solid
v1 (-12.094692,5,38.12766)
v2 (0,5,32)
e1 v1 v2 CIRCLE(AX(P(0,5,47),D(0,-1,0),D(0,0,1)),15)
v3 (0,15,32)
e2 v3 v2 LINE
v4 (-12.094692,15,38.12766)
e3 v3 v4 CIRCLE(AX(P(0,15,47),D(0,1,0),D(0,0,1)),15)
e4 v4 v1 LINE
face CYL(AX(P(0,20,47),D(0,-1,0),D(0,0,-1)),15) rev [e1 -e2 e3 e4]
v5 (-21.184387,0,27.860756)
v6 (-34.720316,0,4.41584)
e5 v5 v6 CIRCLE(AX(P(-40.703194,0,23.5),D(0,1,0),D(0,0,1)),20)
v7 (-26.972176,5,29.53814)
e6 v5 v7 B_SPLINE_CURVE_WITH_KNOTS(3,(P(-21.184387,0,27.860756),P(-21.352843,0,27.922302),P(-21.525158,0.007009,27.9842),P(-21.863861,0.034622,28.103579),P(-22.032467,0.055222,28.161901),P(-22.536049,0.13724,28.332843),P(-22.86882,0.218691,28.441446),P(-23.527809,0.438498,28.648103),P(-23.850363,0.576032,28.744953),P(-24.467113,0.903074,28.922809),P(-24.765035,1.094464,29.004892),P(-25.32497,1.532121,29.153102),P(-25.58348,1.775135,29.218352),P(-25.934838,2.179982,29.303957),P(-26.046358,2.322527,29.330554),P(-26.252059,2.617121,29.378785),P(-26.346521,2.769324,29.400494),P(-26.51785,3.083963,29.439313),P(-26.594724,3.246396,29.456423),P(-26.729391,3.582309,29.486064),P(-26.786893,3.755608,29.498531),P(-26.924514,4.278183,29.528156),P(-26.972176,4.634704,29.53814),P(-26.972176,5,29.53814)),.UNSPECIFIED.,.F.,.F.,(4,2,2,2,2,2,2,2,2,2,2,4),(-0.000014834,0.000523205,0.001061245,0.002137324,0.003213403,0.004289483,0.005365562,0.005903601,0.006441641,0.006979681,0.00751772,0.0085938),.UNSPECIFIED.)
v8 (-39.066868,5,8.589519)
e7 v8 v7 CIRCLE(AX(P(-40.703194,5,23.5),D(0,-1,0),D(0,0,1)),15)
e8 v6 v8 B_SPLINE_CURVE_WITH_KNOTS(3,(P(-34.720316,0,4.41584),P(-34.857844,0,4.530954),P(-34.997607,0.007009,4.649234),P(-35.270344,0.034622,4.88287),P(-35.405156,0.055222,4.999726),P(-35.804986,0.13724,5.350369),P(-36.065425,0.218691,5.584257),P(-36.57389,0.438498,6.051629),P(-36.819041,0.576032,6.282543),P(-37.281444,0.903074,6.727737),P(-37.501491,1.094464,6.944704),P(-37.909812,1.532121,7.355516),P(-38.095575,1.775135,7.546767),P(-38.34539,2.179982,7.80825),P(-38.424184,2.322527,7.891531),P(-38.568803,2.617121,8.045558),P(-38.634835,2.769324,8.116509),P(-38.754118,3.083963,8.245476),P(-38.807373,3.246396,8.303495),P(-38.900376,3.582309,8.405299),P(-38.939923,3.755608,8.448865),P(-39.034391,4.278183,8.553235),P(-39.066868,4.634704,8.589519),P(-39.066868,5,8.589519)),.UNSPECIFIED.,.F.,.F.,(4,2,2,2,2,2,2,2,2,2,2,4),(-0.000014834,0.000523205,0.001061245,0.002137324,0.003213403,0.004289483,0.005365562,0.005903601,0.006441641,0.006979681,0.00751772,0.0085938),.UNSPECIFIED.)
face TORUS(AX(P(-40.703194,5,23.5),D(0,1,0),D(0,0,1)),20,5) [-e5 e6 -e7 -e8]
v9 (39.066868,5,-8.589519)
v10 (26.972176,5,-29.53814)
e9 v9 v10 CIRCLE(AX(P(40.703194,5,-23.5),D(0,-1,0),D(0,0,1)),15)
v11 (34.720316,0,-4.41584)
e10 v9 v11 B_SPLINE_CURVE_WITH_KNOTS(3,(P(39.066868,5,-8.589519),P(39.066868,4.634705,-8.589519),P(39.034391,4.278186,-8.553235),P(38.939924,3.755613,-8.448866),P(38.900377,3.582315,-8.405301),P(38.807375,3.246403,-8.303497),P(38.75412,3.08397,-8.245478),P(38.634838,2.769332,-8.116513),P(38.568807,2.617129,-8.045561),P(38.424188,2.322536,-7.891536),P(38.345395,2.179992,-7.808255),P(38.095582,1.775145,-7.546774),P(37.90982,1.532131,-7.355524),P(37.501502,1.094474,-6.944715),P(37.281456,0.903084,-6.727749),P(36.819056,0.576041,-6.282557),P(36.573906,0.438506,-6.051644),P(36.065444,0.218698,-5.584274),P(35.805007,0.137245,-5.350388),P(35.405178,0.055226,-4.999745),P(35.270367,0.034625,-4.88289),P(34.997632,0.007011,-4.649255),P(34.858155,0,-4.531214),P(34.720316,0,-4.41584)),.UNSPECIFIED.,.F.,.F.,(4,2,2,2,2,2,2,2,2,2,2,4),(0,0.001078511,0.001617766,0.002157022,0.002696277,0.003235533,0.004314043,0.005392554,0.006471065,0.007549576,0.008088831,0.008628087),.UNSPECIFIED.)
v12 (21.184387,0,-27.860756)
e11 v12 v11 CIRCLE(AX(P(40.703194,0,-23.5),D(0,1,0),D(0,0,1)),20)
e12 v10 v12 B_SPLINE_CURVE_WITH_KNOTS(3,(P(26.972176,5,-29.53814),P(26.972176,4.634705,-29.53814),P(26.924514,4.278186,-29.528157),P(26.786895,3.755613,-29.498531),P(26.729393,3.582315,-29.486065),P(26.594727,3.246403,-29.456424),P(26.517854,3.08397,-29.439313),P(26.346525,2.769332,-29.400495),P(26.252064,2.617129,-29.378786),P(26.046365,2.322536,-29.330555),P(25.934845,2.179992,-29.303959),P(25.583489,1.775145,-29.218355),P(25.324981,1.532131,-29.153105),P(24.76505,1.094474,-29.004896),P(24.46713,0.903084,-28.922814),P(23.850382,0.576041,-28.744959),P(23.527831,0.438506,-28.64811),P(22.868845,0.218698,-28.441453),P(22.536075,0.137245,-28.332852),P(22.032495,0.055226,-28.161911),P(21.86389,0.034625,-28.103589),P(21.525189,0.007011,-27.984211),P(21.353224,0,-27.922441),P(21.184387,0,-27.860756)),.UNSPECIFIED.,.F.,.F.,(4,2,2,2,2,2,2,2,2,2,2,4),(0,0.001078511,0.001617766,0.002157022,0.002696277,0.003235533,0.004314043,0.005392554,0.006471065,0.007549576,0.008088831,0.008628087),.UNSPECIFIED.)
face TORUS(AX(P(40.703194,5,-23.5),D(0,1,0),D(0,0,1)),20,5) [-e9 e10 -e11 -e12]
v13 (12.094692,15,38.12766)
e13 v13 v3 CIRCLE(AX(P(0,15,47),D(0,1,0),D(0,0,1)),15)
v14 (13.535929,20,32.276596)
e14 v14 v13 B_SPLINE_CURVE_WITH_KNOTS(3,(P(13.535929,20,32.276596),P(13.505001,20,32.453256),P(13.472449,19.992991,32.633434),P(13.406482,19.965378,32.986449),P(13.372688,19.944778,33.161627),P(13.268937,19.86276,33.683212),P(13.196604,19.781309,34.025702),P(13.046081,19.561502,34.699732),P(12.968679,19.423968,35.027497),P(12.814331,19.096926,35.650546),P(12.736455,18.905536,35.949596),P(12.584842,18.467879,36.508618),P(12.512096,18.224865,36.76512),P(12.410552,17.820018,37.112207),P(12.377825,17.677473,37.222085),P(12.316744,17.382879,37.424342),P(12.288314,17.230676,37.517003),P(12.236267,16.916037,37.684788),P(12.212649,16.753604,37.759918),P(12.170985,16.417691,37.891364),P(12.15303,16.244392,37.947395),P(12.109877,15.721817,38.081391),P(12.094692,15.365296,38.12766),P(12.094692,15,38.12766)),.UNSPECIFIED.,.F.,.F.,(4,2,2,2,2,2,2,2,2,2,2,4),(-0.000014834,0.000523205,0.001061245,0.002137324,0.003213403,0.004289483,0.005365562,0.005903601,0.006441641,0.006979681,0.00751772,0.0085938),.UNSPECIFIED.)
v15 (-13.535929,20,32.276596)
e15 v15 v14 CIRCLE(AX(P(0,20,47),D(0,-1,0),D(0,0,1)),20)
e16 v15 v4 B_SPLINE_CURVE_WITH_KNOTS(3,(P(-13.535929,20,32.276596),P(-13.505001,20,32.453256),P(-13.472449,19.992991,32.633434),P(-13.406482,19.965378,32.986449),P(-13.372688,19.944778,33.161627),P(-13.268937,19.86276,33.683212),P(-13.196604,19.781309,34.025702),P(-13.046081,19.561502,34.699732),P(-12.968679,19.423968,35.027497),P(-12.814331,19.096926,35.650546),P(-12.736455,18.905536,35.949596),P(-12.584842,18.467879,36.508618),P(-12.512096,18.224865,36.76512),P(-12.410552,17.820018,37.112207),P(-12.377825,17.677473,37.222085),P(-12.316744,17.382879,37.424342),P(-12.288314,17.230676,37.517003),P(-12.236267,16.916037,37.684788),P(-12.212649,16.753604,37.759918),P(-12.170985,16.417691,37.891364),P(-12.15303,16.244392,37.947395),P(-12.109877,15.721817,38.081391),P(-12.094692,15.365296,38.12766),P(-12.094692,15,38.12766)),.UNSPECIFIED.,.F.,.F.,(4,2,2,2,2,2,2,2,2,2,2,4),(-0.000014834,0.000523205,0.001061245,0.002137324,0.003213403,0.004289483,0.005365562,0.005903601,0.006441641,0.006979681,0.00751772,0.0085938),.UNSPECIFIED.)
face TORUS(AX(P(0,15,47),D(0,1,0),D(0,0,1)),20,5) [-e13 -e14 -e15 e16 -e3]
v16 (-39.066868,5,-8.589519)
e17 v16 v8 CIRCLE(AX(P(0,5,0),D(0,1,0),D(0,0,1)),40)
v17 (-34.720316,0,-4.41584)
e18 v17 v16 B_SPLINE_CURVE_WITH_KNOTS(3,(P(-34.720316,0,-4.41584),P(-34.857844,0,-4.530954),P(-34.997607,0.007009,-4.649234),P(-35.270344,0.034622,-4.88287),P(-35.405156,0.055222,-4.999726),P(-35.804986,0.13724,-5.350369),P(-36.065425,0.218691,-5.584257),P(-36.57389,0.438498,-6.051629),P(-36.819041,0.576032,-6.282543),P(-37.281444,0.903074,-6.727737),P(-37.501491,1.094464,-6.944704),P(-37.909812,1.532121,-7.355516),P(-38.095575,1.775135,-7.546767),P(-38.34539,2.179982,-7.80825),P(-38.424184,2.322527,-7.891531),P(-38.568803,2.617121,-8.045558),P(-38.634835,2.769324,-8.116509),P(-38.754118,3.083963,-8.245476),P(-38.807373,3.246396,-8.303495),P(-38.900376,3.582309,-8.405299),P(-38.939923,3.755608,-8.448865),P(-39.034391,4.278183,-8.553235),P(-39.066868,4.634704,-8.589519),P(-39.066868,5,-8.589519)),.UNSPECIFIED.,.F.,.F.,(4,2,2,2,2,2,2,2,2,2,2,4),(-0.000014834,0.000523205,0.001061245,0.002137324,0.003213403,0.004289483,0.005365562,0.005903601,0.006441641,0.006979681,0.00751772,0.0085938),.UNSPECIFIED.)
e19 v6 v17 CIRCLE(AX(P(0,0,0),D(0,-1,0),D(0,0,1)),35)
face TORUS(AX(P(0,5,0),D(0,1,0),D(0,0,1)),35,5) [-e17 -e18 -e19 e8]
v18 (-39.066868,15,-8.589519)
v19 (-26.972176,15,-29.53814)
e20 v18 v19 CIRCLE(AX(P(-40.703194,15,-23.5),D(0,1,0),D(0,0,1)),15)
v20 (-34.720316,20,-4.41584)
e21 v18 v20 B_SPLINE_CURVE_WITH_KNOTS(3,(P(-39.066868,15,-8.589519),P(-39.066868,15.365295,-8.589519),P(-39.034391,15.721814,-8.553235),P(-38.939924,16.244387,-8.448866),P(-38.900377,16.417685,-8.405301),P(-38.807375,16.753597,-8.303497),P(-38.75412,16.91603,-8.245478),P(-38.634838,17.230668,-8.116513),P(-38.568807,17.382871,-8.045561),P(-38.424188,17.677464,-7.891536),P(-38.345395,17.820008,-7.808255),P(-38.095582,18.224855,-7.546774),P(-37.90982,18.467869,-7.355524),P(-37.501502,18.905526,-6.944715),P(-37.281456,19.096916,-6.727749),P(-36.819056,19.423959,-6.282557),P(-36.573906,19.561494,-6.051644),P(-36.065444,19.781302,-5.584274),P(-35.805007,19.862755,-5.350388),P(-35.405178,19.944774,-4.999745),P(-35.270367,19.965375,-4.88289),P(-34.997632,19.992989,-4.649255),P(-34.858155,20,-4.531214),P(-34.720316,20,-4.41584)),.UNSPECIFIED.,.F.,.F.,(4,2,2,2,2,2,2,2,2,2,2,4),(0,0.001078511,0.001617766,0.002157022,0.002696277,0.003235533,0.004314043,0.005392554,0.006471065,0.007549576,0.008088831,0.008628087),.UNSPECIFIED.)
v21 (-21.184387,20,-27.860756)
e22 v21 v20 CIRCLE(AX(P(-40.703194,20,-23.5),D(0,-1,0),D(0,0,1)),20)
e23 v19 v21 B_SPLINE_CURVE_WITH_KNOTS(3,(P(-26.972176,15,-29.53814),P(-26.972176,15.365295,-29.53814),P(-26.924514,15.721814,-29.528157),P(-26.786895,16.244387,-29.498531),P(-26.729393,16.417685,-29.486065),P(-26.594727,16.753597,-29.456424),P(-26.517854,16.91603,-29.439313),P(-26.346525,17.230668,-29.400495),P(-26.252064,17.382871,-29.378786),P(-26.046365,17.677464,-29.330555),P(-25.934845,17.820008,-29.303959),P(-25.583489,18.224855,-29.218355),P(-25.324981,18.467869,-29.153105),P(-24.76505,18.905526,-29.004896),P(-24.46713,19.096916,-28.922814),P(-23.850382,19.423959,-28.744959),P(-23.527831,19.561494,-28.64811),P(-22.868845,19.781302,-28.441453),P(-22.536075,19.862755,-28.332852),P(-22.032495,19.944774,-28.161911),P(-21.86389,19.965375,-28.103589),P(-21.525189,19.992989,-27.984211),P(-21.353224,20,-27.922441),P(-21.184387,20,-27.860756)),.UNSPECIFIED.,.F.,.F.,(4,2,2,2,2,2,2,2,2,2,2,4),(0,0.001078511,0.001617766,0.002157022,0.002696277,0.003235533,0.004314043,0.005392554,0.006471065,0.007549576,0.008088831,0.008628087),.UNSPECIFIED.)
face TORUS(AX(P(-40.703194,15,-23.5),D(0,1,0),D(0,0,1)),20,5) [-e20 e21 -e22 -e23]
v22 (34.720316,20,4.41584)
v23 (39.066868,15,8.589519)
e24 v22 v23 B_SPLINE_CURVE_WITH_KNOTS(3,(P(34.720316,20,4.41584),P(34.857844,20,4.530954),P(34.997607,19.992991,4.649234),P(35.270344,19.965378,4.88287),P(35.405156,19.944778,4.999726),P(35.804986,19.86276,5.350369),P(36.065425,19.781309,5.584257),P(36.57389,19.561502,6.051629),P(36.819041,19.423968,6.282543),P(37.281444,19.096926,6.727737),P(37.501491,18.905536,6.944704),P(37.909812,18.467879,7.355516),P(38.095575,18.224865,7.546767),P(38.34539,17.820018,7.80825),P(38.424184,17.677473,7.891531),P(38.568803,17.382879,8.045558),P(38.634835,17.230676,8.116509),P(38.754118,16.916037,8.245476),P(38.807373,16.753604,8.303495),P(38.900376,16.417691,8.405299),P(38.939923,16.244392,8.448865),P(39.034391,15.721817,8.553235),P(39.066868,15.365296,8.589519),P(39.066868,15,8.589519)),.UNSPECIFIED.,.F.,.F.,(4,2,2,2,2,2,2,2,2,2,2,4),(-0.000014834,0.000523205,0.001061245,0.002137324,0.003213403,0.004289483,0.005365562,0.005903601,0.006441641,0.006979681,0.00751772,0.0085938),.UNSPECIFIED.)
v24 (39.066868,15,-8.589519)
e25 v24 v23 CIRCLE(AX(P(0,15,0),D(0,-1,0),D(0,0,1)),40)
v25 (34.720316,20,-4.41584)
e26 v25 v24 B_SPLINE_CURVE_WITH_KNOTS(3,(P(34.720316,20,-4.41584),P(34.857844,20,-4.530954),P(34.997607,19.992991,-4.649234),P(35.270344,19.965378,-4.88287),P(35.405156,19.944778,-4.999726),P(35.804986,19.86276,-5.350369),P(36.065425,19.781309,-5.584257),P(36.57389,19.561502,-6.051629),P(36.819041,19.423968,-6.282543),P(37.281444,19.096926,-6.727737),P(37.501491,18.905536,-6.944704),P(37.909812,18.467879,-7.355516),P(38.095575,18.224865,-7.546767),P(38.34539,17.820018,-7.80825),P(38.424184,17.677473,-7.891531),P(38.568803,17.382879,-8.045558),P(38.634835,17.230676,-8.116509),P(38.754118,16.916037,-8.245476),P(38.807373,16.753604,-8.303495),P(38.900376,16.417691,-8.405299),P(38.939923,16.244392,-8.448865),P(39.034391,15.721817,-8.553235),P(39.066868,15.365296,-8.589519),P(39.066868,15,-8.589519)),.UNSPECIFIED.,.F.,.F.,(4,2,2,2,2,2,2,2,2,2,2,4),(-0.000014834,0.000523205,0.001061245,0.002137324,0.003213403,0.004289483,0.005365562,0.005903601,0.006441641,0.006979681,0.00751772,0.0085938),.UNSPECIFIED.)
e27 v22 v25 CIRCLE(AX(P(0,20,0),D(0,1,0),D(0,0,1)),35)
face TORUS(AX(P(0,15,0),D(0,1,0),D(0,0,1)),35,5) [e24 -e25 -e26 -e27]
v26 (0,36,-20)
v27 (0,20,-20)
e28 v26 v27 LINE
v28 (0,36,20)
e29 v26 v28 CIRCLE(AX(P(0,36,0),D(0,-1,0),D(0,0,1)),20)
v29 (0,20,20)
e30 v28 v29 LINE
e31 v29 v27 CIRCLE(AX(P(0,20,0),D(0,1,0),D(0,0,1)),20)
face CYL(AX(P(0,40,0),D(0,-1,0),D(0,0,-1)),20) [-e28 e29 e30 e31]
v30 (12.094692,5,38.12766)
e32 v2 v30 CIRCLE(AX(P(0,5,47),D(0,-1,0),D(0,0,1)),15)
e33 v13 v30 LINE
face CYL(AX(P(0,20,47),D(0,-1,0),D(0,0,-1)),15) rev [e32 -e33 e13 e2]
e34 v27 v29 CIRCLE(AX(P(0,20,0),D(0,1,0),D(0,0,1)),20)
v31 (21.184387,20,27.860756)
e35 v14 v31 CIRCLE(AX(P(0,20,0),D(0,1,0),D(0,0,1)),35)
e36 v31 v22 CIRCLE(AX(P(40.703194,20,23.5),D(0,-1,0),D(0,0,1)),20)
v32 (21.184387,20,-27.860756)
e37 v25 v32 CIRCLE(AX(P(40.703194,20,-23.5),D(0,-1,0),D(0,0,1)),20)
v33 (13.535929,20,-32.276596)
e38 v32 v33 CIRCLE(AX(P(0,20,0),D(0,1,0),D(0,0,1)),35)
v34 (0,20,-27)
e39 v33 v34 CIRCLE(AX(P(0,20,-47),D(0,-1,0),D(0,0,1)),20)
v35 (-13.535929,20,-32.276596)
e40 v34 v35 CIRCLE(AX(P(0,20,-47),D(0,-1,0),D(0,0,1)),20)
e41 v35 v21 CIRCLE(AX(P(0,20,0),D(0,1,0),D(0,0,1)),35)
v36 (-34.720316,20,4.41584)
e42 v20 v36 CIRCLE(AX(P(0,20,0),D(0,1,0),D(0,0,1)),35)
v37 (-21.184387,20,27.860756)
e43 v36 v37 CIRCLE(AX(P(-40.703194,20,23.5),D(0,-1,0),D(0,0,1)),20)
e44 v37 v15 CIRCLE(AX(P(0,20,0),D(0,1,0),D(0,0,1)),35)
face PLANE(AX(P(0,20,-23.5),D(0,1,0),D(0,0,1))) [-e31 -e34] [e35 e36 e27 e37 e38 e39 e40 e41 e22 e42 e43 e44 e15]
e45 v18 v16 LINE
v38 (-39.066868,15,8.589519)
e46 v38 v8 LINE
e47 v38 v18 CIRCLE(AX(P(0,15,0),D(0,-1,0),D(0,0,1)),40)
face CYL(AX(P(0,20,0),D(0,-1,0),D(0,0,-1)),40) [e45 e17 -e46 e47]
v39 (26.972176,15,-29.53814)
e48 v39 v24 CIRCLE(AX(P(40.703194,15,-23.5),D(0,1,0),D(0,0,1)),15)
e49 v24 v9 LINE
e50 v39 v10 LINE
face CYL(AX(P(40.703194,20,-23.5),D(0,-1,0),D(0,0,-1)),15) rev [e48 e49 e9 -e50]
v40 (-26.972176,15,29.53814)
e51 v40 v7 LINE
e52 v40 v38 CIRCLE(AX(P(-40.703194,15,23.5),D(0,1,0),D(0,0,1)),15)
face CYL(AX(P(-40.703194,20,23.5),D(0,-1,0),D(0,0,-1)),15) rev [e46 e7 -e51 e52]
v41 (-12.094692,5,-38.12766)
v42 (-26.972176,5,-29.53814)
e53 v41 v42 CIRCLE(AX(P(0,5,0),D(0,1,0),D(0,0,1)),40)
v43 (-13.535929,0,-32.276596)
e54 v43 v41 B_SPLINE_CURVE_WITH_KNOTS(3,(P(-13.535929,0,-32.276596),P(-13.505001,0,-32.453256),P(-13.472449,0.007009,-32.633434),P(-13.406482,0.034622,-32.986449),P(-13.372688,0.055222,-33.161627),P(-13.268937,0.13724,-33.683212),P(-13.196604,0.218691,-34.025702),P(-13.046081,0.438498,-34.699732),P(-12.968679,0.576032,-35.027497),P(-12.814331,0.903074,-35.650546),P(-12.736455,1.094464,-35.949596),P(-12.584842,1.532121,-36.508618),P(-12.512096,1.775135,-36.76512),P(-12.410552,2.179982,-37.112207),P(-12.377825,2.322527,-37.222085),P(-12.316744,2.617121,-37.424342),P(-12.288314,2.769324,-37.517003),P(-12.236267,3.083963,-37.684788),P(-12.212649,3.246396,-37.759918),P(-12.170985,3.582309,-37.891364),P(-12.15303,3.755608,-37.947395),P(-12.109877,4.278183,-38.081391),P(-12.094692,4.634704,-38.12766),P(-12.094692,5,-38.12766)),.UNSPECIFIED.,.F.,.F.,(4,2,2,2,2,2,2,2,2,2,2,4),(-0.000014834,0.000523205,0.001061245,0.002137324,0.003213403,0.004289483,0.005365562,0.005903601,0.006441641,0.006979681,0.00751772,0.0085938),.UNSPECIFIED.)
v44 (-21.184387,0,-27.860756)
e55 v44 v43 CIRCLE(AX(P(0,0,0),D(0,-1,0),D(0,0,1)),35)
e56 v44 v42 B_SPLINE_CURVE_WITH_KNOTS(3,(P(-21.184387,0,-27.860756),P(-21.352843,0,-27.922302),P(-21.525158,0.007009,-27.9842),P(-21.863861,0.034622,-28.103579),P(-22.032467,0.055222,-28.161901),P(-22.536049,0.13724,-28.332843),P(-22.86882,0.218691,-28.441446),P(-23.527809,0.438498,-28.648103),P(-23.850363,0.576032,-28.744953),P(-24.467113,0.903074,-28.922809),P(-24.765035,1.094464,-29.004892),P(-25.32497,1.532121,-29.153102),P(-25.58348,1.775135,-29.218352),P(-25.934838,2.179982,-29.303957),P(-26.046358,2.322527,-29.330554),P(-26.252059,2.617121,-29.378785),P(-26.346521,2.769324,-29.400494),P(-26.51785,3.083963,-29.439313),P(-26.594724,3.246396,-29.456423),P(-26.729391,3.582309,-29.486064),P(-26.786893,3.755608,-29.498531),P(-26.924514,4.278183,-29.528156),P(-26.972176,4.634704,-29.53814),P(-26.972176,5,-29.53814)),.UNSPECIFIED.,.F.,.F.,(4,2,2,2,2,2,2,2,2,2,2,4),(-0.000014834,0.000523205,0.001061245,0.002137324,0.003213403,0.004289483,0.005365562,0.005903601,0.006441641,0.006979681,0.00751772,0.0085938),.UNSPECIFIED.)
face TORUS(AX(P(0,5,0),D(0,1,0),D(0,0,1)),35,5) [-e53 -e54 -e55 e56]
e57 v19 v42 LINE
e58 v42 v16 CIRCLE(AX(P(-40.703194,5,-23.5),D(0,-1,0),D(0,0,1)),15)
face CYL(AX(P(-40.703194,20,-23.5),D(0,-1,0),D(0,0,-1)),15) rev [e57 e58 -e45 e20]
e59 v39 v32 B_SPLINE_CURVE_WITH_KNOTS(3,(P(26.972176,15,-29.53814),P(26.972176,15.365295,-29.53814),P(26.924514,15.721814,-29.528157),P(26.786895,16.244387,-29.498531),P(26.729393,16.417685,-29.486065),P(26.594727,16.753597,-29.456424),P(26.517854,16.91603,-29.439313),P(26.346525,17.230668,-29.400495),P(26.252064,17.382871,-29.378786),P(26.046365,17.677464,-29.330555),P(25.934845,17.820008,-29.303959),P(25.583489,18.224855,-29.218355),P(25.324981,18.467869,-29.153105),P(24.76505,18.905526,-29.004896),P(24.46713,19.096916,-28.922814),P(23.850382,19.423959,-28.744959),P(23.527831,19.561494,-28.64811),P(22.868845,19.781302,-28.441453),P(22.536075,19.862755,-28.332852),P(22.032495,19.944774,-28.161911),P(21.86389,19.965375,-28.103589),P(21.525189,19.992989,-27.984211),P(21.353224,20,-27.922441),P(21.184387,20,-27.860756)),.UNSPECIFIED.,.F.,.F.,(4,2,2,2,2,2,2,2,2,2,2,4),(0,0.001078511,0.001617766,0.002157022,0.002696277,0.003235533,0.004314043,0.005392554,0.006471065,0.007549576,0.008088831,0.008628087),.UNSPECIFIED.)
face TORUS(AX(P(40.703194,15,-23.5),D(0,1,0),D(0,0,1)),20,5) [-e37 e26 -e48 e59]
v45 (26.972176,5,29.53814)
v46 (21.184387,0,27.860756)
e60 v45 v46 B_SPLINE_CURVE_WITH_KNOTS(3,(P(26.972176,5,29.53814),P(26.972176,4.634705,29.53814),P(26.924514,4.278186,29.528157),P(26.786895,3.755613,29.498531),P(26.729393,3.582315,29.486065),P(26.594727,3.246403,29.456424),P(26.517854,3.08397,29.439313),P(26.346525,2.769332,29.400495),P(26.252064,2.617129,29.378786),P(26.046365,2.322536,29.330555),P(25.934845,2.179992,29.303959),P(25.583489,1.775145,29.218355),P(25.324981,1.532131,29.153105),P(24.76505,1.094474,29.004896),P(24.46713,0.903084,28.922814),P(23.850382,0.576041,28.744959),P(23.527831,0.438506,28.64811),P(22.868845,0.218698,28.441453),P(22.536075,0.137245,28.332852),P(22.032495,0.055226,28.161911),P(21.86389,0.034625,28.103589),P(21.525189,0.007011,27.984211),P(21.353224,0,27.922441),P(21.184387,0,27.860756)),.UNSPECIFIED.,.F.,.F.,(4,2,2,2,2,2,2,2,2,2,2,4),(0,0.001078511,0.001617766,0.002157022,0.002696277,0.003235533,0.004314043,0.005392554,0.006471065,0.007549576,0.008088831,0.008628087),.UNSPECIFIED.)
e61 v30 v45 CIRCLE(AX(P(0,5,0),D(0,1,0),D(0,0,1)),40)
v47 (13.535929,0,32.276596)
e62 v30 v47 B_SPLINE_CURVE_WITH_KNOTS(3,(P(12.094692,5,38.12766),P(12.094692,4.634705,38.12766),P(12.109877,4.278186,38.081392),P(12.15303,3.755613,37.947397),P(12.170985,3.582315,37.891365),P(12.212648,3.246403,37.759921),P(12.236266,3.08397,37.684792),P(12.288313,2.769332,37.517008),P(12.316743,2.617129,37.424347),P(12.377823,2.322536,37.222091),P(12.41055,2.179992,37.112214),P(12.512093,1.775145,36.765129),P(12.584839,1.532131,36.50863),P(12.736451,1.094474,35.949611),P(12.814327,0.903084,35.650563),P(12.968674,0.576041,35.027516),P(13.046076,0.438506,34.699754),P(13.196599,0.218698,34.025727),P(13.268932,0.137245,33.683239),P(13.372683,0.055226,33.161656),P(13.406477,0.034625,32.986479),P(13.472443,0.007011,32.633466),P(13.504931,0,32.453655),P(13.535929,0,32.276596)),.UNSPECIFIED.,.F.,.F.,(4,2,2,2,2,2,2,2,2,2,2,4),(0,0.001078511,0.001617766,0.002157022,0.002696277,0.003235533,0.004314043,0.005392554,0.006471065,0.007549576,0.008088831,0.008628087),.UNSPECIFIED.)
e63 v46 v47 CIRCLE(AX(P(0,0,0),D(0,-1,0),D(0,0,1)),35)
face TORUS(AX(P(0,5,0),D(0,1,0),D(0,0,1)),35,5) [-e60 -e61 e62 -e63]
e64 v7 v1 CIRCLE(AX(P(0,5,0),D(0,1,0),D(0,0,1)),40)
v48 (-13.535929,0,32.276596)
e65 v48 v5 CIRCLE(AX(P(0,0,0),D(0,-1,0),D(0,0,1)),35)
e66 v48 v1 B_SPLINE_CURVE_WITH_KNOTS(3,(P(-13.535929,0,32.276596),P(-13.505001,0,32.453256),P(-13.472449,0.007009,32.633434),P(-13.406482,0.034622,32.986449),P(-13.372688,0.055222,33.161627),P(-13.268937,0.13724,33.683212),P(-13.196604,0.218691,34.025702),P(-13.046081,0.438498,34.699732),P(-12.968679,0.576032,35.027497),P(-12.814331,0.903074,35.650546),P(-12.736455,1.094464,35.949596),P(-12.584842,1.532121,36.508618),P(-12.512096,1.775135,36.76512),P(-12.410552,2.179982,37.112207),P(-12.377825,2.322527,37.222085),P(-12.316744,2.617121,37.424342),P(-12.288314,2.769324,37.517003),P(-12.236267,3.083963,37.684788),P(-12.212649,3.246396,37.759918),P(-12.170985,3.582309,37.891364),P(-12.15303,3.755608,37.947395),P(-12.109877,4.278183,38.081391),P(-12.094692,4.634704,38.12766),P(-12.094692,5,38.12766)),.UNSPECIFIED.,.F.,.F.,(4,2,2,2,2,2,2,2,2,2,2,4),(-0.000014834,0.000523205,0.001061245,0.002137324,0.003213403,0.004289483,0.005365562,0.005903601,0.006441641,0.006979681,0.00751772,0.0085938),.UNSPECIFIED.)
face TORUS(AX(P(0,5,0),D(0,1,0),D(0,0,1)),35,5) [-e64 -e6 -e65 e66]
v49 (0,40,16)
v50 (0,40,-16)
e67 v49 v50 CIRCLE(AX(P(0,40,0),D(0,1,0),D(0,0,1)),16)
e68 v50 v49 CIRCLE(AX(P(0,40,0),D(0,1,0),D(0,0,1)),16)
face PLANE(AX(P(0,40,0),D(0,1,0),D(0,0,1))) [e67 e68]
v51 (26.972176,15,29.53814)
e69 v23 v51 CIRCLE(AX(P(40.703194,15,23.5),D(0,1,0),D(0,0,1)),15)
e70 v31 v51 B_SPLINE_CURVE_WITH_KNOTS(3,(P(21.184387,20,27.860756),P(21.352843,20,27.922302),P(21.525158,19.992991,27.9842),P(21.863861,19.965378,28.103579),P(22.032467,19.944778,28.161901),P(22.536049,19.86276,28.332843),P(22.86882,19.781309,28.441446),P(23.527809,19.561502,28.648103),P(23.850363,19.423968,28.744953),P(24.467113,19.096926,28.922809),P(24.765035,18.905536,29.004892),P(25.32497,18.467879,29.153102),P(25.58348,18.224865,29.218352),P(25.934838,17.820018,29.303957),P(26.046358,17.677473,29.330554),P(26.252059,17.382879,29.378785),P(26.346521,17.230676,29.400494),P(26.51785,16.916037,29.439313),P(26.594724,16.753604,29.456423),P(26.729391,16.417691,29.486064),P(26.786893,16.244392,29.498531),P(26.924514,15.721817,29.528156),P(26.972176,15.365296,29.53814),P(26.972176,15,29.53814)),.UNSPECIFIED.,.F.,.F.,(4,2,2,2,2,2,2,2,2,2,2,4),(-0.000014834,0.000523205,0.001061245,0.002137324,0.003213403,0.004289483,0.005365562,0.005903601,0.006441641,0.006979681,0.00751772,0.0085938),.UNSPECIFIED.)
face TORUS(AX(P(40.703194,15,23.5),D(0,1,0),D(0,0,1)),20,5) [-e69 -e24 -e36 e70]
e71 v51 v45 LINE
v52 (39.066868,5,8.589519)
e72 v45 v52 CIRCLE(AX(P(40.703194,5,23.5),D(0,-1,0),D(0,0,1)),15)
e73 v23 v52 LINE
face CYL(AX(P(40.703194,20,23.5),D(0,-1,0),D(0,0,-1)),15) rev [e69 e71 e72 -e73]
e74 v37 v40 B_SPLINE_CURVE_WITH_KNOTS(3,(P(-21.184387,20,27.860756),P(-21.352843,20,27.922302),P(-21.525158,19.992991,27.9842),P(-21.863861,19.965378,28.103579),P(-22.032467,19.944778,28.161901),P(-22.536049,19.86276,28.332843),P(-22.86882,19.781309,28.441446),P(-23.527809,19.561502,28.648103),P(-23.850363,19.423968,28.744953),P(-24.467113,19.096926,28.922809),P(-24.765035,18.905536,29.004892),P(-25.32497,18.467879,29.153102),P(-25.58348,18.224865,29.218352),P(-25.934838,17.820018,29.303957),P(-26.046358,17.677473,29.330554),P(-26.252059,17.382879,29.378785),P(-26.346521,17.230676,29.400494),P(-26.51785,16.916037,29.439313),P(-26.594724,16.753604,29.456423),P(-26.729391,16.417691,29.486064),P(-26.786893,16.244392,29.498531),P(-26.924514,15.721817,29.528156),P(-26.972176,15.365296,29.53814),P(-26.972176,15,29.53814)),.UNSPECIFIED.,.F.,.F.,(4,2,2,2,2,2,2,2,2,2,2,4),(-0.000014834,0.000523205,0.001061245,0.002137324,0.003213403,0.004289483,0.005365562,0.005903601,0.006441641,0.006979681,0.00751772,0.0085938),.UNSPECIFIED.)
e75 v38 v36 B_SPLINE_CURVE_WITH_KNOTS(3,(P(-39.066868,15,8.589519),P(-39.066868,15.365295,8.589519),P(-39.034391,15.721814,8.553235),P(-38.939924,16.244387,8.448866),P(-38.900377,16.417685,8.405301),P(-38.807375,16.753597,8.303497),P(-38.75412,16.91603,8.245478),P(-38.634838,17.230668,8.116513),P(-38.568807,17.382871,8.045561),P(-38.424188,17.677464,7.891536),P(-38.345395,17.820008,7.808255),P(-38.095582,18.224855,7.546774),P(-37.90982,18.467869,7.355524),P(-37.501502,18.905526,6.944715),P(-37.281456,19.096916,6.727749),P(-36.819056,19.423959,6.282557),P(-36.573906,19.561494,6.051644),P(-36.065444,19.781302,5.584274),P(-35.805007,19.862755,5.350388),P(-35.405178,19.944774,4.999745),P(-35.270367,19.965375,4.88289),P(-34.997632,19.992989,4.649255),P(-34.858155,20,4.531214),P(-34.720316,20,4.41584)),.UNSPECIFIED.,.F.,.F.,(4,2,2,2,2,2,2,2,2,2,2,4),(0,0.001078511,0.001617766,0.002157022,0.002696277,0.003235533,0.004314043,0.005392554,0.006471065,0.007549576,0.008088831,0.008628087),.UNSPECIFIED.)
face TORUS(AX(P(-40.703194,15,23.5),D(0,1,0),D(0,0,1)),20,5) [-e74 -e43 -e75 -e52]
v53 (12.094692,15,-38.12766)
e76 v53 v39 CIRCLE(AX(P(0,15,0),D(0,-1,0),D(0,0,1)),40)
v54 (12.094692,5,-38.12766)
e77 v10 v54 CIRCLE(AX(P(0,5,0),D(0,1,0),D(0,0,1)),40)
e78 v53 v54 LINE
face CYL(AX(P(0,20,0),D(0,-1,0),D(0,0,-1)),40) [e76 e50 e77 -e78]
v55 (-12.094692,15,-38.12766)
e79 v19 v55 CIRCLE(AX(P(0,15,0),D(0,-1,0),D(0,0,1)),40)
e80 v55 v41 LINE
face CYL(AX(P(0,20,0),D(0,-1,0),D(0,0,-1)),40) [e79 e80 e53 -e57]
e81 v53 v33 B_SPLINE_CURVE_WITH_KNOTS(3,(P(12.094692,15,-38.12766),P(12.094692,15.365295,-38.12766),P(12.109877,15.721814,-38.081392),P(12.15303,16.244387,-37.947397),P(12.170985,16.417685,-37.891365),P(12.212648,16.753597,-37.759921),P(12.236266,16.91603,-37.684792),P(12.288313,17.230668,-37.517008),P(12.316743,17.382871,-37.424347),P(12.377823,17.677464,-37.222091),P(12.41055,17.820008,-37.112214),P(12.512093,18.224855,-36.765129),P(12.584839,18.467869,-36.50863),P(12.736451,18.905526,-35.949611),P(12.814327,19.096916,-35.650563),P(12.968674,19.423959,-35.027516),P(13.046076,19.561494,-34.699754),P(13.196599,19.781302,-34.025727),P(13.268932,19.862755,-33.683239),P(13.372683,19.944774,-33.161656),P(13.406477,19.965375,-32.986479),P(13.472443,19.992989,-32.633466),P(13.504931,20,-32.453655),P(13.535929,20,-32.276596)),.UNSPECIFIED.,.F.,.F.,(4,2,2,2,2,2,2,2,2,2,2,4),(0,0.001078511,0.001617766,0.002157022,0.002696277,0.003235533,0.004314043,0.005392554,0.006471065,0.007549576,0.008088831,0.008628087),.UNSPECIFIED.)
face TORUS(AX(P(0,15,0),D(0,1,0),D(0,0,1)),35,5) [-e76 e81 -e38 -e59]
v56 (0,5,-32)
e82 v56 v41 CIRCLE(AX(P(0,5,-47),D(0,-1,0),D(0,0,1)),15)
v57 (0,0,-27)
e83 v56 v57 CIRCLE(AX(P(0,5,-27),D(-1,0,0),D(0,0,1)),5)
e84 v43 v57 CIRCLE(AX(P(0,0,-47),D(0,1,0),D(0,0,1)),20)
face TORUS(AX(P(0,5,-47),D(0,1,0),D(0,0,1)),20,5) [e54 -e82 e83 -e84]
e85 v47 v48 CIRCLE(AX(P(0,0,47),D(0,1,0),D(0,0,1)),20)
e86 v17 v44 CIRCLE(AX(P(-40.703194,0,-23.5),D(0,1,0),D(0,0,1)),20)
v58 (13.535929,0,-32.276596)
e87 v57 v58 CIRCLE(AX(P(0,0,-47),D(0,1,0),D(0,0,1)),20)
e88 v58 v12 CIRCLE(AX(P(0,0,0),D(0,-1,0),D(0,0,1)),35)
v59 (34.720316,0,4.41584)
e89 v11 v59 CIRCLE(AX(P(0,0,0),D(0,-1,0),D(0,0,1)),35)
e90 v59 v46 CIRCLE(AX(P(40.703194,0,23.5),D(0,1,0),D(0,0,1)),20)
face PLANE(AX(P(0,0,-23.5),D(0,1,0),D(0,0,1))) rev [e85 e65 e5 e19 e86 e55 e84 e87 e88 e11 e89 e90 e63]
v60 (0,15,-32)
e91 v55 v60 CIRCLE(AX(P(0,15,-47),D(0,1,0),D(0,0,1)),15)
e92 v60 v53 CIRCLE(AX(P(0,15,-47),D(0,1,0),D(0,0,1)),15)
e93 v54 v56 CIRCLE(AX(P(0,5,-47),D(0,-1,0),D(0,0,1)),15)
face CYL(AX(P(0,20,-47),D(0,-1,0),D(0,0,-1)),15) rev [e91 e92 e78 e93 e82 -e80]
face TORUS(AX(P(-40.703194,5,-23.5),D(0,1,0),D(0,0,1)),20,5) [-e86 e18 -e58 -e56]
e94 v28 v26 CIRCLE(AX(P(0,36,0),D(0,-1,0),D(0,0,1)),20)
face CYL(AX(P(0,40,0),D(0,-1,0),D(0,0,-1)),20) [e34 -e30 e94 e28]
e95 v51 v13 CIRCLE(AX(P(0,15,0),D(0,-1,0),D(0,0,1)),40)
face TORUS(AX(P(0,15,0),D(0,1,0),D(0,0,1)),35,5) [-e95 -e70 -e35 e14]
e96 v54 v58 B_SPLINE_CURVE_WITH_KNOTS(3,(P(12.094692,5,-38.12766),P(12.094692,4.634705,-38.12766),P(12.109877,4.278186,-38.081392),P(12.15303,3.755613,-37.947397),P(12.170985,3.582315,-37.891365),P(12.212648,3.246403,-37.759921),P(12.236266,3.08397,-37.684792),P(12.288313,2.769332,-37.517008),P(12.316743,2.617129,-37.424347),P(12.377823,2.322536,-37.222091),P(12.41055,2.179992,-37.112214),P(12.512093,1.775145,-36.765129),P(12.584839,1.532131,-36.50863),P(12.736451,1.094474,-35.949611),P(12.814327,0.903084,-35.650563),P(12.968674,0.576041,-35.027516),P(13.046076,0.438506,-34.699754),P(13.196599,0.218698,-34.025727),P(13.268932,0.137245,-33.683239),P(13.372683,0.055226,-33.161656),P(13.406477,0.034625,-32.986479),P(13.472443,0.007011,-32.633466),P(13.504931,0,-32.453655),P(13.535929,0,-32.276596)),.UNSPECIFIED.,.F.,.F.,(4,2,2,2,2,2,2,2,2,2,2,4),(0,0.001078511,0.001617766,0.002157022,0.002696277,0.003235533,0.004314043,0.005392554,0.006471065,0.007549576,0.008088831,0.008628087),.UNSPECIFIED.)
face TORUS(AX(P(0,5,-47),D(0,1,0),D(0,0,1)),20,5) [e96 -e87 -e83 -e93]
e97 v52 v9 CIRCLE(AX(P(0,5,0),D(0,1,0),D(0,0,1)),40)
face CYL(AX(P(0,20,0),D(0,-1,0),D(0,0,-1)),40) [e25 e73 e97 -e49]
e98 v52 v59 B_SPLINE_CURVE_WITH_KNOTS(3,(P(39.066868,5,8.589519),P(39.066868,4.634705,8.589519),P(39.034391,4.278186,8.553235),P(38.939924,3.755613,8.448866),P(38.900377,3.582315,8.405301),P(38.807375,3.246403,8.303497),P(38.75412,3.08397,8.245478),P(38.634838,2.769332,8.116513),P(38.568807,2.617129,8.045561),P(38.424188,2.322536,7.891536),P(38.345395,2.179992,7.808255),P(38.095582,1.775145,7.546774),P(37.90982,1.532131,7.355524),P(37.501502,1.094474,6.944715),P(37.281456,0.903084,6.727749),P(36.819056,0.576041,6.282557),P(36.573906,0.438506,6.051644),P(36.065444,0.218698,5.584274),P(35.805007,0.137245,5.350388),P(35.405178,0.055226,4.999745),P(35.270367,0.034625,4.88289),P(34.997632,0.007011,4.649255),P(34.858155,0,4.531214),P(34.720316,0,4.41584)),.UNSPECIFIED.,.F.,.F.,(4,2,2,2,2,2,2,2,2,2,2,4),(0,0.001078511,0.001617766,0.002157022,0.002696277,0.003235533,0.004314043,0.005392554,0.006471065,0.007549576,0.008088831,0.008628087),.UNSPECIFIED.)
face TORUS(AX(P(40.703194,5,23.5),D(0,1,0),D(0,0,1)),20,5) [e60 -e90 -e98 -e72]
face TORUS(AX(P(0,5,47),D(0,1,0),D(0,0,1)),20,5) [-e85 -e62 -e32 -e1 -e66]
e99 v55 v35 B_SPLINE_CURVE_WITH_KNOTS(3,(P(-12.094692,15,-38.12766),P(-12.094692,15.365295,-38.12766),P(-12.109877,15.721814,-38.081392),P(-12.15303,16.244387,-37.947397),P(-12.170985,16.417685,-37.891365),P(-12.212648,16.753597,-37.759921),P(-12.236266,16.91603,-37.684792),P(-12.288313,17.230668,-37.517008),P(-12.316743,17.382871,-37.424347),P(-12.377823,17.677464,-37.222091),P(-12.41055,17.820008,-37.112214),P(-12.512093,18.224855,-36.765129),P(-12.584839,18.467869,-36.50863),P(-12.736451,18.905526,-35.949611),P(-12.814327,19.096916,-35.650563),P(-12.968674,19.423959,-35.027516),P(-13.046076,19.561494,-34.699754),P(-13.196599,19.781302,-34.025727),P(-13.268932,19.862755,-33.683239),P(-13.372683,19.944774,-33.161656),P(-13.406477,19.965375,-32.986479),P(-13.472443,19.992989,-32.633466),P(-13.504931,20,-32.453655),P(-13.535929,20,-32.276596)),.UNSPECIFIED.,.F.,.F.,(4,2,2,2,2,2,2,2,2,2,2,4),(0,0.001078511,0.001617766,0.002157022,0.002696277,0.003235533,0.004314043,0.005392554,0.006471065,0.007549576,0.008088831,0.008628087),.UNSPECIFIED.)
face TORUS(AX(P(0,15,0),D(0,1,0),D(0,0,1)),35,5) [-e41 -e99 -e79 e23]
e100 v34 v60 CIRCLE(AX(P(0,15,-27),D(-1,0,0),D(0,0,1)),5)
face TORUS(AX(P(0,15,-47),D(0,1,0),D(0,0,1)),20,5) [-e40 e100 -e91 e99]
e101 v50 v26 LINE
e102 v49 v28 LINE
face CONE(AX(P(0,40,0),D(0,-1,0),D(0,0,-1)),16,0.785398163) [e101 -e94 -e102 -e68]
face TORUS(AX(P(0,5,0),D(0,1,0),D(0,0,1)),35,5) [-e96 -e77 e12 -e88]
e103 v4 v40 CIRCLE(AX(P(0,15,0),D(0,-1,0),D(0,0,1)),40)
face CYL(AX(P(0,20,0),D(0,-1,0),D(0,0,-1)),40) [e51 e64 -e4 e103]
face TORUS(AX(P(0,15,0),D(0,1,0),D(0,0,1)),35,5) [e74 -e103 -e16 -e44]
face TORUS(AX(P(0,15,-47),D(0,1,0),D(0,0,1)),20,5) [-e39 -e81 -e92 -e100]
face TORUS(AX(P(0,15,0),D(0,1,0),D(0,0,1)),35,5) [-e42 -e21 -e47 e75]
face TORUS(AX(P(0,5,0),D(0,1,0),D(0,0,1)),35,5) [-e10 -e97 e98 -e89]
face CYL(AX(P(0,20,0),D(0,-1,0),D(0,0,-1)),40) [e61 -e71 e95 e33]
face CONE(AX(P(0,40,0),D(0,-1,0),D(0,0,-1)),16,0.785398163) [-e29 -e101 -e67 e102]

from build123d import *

# Parameters (mm, degrees)
STAR_GRIP_BODY_DEPTH      = 20
GRIP_EDGE_FILLET_R5_R     = 5
HUB_SKETCH_40_R           = 20
HUB_40_DEPTH              = 20
HUB_TOP_CHAMFER_4X45_SIZE = 4


with BuildPart() as part:
    # Star Profile Sketch → Star Grip Body (new body)
    with BuildSketch(Plane(origin=(0, 0, 0), x_dir=(1, 0, 0), z_dir=(0, 1, 0))):
        with BuildLine():
            ThreePointArc((-12.094692033, 38.127659574), (-20, 34.641016151), (-26.972175762, 29.538140339))
            ThreePointArc((-26.972175762, 29.538140339), (-27.712812921, 16), (-39.066867795, 8.589519236))
            ThreePointArc((-39.066867795, 8.589519236), (-40, 0), (-39.066867795, -8.589519236))
            ThreePointArc((-39.066867795, -8.589519236), (-27.712812921, -16), (-26.972175762, -29.538140339))
            ThreePointArc((-26.972175762, -29.538140339), (-20, -34.641016151), (-12.094692033, -38.127659574))
            ThreePointArc((-12.094692033, -38.127659574), (0, -32), (12.094692033, -38.127659574))
            ThreePointArc((12.094692033, -38.127659574), (20, -34.641016151), (26.972175762, -29.538140339))
            ThreePointArc((26.972175762, -29.538140339), (27.712812921, -16), (39.066867795, -8.589519236))
            ThreePointArc((39.066867795, -8.589519236), (40, 0), (39.066867795, 8.589519236))
            ThreePointArc((39.066867795, 8.589519236), (27.712812921, 16), (26.972175762, 29.538140339))
            ThreePointArc((26.972175762, 29.538140339), (20, 34.641016151), (12.094692033, 38.127659574))
            ThreePointArc((12.094692033, 38.127659574), (0, 32), (-12.094692033, 38.127659574))
        make_face()
    extrude(amount=STAR_GRIP_BODY_DEPTH)

    # Grip Edge Fillet R5
    grip_edge_fillet_r5_edges = [part.edges().sort_by_distance(p)[0] for p in [
        (27.712812921, 0, -16),
        (40, 0, 0),
        (-20, 20, -34.641016151),
        (27.712812921, 0, 16),
        (20, 0, 34.641016151),
        (0, 0, 32),
        (-20, 0, 34.641016151),
        (-27.712812921, 0, 16),
        (-40, 0, 0),
        (-27.712812921, 0, -16),
        (-20, 0, -34.641016151),
        (0, 0, -32),
        (20, 0, -34.641016151),
        (-27.712812921, 20, -16),
        (-40, 20, 0),
        (-27.712812921, 20, 16),
        (-20, 20, 34.641016151),
        (0, 20, 32),
        (20, 20, 34.641016151),
        (27.712812921, 20, 16),
        (40, 20, 0),
        (27.712812921, 20, -16),
        (20, 20, -34.641016151),
        (0, 20, -32),
    ]]
    fillet(grip_edge_fillet_r5_edges, radius=GRIP_EDGE_FILLET_R5_R)

    # Hub Sketch Ø40 → Hub Ø40 (add)
    with BuildSketch(Plane(origin=(0, 20, 0), x_dir=(1, 0, 0), z_dir=(0, 1, 0))):
        with Locations(Location((0, 0, 0), (0, 0, 270))):
            Circle(HUB_SKETCH_40_R)
    extrude(amount=HUB_40_DEPTH)

    # Hub Top Chamfer 4x45°
    hub_top_chamfer_4x45_edges = [part.edges().sort_by_distance(p)[0] for p in [
        (0, 40, -20),
    ]]
    chamfer(hub_top_chamfer_4x45_edges, length=HUB_TOP_CHAMFER_4X45_SIZE)


solid = part.part
